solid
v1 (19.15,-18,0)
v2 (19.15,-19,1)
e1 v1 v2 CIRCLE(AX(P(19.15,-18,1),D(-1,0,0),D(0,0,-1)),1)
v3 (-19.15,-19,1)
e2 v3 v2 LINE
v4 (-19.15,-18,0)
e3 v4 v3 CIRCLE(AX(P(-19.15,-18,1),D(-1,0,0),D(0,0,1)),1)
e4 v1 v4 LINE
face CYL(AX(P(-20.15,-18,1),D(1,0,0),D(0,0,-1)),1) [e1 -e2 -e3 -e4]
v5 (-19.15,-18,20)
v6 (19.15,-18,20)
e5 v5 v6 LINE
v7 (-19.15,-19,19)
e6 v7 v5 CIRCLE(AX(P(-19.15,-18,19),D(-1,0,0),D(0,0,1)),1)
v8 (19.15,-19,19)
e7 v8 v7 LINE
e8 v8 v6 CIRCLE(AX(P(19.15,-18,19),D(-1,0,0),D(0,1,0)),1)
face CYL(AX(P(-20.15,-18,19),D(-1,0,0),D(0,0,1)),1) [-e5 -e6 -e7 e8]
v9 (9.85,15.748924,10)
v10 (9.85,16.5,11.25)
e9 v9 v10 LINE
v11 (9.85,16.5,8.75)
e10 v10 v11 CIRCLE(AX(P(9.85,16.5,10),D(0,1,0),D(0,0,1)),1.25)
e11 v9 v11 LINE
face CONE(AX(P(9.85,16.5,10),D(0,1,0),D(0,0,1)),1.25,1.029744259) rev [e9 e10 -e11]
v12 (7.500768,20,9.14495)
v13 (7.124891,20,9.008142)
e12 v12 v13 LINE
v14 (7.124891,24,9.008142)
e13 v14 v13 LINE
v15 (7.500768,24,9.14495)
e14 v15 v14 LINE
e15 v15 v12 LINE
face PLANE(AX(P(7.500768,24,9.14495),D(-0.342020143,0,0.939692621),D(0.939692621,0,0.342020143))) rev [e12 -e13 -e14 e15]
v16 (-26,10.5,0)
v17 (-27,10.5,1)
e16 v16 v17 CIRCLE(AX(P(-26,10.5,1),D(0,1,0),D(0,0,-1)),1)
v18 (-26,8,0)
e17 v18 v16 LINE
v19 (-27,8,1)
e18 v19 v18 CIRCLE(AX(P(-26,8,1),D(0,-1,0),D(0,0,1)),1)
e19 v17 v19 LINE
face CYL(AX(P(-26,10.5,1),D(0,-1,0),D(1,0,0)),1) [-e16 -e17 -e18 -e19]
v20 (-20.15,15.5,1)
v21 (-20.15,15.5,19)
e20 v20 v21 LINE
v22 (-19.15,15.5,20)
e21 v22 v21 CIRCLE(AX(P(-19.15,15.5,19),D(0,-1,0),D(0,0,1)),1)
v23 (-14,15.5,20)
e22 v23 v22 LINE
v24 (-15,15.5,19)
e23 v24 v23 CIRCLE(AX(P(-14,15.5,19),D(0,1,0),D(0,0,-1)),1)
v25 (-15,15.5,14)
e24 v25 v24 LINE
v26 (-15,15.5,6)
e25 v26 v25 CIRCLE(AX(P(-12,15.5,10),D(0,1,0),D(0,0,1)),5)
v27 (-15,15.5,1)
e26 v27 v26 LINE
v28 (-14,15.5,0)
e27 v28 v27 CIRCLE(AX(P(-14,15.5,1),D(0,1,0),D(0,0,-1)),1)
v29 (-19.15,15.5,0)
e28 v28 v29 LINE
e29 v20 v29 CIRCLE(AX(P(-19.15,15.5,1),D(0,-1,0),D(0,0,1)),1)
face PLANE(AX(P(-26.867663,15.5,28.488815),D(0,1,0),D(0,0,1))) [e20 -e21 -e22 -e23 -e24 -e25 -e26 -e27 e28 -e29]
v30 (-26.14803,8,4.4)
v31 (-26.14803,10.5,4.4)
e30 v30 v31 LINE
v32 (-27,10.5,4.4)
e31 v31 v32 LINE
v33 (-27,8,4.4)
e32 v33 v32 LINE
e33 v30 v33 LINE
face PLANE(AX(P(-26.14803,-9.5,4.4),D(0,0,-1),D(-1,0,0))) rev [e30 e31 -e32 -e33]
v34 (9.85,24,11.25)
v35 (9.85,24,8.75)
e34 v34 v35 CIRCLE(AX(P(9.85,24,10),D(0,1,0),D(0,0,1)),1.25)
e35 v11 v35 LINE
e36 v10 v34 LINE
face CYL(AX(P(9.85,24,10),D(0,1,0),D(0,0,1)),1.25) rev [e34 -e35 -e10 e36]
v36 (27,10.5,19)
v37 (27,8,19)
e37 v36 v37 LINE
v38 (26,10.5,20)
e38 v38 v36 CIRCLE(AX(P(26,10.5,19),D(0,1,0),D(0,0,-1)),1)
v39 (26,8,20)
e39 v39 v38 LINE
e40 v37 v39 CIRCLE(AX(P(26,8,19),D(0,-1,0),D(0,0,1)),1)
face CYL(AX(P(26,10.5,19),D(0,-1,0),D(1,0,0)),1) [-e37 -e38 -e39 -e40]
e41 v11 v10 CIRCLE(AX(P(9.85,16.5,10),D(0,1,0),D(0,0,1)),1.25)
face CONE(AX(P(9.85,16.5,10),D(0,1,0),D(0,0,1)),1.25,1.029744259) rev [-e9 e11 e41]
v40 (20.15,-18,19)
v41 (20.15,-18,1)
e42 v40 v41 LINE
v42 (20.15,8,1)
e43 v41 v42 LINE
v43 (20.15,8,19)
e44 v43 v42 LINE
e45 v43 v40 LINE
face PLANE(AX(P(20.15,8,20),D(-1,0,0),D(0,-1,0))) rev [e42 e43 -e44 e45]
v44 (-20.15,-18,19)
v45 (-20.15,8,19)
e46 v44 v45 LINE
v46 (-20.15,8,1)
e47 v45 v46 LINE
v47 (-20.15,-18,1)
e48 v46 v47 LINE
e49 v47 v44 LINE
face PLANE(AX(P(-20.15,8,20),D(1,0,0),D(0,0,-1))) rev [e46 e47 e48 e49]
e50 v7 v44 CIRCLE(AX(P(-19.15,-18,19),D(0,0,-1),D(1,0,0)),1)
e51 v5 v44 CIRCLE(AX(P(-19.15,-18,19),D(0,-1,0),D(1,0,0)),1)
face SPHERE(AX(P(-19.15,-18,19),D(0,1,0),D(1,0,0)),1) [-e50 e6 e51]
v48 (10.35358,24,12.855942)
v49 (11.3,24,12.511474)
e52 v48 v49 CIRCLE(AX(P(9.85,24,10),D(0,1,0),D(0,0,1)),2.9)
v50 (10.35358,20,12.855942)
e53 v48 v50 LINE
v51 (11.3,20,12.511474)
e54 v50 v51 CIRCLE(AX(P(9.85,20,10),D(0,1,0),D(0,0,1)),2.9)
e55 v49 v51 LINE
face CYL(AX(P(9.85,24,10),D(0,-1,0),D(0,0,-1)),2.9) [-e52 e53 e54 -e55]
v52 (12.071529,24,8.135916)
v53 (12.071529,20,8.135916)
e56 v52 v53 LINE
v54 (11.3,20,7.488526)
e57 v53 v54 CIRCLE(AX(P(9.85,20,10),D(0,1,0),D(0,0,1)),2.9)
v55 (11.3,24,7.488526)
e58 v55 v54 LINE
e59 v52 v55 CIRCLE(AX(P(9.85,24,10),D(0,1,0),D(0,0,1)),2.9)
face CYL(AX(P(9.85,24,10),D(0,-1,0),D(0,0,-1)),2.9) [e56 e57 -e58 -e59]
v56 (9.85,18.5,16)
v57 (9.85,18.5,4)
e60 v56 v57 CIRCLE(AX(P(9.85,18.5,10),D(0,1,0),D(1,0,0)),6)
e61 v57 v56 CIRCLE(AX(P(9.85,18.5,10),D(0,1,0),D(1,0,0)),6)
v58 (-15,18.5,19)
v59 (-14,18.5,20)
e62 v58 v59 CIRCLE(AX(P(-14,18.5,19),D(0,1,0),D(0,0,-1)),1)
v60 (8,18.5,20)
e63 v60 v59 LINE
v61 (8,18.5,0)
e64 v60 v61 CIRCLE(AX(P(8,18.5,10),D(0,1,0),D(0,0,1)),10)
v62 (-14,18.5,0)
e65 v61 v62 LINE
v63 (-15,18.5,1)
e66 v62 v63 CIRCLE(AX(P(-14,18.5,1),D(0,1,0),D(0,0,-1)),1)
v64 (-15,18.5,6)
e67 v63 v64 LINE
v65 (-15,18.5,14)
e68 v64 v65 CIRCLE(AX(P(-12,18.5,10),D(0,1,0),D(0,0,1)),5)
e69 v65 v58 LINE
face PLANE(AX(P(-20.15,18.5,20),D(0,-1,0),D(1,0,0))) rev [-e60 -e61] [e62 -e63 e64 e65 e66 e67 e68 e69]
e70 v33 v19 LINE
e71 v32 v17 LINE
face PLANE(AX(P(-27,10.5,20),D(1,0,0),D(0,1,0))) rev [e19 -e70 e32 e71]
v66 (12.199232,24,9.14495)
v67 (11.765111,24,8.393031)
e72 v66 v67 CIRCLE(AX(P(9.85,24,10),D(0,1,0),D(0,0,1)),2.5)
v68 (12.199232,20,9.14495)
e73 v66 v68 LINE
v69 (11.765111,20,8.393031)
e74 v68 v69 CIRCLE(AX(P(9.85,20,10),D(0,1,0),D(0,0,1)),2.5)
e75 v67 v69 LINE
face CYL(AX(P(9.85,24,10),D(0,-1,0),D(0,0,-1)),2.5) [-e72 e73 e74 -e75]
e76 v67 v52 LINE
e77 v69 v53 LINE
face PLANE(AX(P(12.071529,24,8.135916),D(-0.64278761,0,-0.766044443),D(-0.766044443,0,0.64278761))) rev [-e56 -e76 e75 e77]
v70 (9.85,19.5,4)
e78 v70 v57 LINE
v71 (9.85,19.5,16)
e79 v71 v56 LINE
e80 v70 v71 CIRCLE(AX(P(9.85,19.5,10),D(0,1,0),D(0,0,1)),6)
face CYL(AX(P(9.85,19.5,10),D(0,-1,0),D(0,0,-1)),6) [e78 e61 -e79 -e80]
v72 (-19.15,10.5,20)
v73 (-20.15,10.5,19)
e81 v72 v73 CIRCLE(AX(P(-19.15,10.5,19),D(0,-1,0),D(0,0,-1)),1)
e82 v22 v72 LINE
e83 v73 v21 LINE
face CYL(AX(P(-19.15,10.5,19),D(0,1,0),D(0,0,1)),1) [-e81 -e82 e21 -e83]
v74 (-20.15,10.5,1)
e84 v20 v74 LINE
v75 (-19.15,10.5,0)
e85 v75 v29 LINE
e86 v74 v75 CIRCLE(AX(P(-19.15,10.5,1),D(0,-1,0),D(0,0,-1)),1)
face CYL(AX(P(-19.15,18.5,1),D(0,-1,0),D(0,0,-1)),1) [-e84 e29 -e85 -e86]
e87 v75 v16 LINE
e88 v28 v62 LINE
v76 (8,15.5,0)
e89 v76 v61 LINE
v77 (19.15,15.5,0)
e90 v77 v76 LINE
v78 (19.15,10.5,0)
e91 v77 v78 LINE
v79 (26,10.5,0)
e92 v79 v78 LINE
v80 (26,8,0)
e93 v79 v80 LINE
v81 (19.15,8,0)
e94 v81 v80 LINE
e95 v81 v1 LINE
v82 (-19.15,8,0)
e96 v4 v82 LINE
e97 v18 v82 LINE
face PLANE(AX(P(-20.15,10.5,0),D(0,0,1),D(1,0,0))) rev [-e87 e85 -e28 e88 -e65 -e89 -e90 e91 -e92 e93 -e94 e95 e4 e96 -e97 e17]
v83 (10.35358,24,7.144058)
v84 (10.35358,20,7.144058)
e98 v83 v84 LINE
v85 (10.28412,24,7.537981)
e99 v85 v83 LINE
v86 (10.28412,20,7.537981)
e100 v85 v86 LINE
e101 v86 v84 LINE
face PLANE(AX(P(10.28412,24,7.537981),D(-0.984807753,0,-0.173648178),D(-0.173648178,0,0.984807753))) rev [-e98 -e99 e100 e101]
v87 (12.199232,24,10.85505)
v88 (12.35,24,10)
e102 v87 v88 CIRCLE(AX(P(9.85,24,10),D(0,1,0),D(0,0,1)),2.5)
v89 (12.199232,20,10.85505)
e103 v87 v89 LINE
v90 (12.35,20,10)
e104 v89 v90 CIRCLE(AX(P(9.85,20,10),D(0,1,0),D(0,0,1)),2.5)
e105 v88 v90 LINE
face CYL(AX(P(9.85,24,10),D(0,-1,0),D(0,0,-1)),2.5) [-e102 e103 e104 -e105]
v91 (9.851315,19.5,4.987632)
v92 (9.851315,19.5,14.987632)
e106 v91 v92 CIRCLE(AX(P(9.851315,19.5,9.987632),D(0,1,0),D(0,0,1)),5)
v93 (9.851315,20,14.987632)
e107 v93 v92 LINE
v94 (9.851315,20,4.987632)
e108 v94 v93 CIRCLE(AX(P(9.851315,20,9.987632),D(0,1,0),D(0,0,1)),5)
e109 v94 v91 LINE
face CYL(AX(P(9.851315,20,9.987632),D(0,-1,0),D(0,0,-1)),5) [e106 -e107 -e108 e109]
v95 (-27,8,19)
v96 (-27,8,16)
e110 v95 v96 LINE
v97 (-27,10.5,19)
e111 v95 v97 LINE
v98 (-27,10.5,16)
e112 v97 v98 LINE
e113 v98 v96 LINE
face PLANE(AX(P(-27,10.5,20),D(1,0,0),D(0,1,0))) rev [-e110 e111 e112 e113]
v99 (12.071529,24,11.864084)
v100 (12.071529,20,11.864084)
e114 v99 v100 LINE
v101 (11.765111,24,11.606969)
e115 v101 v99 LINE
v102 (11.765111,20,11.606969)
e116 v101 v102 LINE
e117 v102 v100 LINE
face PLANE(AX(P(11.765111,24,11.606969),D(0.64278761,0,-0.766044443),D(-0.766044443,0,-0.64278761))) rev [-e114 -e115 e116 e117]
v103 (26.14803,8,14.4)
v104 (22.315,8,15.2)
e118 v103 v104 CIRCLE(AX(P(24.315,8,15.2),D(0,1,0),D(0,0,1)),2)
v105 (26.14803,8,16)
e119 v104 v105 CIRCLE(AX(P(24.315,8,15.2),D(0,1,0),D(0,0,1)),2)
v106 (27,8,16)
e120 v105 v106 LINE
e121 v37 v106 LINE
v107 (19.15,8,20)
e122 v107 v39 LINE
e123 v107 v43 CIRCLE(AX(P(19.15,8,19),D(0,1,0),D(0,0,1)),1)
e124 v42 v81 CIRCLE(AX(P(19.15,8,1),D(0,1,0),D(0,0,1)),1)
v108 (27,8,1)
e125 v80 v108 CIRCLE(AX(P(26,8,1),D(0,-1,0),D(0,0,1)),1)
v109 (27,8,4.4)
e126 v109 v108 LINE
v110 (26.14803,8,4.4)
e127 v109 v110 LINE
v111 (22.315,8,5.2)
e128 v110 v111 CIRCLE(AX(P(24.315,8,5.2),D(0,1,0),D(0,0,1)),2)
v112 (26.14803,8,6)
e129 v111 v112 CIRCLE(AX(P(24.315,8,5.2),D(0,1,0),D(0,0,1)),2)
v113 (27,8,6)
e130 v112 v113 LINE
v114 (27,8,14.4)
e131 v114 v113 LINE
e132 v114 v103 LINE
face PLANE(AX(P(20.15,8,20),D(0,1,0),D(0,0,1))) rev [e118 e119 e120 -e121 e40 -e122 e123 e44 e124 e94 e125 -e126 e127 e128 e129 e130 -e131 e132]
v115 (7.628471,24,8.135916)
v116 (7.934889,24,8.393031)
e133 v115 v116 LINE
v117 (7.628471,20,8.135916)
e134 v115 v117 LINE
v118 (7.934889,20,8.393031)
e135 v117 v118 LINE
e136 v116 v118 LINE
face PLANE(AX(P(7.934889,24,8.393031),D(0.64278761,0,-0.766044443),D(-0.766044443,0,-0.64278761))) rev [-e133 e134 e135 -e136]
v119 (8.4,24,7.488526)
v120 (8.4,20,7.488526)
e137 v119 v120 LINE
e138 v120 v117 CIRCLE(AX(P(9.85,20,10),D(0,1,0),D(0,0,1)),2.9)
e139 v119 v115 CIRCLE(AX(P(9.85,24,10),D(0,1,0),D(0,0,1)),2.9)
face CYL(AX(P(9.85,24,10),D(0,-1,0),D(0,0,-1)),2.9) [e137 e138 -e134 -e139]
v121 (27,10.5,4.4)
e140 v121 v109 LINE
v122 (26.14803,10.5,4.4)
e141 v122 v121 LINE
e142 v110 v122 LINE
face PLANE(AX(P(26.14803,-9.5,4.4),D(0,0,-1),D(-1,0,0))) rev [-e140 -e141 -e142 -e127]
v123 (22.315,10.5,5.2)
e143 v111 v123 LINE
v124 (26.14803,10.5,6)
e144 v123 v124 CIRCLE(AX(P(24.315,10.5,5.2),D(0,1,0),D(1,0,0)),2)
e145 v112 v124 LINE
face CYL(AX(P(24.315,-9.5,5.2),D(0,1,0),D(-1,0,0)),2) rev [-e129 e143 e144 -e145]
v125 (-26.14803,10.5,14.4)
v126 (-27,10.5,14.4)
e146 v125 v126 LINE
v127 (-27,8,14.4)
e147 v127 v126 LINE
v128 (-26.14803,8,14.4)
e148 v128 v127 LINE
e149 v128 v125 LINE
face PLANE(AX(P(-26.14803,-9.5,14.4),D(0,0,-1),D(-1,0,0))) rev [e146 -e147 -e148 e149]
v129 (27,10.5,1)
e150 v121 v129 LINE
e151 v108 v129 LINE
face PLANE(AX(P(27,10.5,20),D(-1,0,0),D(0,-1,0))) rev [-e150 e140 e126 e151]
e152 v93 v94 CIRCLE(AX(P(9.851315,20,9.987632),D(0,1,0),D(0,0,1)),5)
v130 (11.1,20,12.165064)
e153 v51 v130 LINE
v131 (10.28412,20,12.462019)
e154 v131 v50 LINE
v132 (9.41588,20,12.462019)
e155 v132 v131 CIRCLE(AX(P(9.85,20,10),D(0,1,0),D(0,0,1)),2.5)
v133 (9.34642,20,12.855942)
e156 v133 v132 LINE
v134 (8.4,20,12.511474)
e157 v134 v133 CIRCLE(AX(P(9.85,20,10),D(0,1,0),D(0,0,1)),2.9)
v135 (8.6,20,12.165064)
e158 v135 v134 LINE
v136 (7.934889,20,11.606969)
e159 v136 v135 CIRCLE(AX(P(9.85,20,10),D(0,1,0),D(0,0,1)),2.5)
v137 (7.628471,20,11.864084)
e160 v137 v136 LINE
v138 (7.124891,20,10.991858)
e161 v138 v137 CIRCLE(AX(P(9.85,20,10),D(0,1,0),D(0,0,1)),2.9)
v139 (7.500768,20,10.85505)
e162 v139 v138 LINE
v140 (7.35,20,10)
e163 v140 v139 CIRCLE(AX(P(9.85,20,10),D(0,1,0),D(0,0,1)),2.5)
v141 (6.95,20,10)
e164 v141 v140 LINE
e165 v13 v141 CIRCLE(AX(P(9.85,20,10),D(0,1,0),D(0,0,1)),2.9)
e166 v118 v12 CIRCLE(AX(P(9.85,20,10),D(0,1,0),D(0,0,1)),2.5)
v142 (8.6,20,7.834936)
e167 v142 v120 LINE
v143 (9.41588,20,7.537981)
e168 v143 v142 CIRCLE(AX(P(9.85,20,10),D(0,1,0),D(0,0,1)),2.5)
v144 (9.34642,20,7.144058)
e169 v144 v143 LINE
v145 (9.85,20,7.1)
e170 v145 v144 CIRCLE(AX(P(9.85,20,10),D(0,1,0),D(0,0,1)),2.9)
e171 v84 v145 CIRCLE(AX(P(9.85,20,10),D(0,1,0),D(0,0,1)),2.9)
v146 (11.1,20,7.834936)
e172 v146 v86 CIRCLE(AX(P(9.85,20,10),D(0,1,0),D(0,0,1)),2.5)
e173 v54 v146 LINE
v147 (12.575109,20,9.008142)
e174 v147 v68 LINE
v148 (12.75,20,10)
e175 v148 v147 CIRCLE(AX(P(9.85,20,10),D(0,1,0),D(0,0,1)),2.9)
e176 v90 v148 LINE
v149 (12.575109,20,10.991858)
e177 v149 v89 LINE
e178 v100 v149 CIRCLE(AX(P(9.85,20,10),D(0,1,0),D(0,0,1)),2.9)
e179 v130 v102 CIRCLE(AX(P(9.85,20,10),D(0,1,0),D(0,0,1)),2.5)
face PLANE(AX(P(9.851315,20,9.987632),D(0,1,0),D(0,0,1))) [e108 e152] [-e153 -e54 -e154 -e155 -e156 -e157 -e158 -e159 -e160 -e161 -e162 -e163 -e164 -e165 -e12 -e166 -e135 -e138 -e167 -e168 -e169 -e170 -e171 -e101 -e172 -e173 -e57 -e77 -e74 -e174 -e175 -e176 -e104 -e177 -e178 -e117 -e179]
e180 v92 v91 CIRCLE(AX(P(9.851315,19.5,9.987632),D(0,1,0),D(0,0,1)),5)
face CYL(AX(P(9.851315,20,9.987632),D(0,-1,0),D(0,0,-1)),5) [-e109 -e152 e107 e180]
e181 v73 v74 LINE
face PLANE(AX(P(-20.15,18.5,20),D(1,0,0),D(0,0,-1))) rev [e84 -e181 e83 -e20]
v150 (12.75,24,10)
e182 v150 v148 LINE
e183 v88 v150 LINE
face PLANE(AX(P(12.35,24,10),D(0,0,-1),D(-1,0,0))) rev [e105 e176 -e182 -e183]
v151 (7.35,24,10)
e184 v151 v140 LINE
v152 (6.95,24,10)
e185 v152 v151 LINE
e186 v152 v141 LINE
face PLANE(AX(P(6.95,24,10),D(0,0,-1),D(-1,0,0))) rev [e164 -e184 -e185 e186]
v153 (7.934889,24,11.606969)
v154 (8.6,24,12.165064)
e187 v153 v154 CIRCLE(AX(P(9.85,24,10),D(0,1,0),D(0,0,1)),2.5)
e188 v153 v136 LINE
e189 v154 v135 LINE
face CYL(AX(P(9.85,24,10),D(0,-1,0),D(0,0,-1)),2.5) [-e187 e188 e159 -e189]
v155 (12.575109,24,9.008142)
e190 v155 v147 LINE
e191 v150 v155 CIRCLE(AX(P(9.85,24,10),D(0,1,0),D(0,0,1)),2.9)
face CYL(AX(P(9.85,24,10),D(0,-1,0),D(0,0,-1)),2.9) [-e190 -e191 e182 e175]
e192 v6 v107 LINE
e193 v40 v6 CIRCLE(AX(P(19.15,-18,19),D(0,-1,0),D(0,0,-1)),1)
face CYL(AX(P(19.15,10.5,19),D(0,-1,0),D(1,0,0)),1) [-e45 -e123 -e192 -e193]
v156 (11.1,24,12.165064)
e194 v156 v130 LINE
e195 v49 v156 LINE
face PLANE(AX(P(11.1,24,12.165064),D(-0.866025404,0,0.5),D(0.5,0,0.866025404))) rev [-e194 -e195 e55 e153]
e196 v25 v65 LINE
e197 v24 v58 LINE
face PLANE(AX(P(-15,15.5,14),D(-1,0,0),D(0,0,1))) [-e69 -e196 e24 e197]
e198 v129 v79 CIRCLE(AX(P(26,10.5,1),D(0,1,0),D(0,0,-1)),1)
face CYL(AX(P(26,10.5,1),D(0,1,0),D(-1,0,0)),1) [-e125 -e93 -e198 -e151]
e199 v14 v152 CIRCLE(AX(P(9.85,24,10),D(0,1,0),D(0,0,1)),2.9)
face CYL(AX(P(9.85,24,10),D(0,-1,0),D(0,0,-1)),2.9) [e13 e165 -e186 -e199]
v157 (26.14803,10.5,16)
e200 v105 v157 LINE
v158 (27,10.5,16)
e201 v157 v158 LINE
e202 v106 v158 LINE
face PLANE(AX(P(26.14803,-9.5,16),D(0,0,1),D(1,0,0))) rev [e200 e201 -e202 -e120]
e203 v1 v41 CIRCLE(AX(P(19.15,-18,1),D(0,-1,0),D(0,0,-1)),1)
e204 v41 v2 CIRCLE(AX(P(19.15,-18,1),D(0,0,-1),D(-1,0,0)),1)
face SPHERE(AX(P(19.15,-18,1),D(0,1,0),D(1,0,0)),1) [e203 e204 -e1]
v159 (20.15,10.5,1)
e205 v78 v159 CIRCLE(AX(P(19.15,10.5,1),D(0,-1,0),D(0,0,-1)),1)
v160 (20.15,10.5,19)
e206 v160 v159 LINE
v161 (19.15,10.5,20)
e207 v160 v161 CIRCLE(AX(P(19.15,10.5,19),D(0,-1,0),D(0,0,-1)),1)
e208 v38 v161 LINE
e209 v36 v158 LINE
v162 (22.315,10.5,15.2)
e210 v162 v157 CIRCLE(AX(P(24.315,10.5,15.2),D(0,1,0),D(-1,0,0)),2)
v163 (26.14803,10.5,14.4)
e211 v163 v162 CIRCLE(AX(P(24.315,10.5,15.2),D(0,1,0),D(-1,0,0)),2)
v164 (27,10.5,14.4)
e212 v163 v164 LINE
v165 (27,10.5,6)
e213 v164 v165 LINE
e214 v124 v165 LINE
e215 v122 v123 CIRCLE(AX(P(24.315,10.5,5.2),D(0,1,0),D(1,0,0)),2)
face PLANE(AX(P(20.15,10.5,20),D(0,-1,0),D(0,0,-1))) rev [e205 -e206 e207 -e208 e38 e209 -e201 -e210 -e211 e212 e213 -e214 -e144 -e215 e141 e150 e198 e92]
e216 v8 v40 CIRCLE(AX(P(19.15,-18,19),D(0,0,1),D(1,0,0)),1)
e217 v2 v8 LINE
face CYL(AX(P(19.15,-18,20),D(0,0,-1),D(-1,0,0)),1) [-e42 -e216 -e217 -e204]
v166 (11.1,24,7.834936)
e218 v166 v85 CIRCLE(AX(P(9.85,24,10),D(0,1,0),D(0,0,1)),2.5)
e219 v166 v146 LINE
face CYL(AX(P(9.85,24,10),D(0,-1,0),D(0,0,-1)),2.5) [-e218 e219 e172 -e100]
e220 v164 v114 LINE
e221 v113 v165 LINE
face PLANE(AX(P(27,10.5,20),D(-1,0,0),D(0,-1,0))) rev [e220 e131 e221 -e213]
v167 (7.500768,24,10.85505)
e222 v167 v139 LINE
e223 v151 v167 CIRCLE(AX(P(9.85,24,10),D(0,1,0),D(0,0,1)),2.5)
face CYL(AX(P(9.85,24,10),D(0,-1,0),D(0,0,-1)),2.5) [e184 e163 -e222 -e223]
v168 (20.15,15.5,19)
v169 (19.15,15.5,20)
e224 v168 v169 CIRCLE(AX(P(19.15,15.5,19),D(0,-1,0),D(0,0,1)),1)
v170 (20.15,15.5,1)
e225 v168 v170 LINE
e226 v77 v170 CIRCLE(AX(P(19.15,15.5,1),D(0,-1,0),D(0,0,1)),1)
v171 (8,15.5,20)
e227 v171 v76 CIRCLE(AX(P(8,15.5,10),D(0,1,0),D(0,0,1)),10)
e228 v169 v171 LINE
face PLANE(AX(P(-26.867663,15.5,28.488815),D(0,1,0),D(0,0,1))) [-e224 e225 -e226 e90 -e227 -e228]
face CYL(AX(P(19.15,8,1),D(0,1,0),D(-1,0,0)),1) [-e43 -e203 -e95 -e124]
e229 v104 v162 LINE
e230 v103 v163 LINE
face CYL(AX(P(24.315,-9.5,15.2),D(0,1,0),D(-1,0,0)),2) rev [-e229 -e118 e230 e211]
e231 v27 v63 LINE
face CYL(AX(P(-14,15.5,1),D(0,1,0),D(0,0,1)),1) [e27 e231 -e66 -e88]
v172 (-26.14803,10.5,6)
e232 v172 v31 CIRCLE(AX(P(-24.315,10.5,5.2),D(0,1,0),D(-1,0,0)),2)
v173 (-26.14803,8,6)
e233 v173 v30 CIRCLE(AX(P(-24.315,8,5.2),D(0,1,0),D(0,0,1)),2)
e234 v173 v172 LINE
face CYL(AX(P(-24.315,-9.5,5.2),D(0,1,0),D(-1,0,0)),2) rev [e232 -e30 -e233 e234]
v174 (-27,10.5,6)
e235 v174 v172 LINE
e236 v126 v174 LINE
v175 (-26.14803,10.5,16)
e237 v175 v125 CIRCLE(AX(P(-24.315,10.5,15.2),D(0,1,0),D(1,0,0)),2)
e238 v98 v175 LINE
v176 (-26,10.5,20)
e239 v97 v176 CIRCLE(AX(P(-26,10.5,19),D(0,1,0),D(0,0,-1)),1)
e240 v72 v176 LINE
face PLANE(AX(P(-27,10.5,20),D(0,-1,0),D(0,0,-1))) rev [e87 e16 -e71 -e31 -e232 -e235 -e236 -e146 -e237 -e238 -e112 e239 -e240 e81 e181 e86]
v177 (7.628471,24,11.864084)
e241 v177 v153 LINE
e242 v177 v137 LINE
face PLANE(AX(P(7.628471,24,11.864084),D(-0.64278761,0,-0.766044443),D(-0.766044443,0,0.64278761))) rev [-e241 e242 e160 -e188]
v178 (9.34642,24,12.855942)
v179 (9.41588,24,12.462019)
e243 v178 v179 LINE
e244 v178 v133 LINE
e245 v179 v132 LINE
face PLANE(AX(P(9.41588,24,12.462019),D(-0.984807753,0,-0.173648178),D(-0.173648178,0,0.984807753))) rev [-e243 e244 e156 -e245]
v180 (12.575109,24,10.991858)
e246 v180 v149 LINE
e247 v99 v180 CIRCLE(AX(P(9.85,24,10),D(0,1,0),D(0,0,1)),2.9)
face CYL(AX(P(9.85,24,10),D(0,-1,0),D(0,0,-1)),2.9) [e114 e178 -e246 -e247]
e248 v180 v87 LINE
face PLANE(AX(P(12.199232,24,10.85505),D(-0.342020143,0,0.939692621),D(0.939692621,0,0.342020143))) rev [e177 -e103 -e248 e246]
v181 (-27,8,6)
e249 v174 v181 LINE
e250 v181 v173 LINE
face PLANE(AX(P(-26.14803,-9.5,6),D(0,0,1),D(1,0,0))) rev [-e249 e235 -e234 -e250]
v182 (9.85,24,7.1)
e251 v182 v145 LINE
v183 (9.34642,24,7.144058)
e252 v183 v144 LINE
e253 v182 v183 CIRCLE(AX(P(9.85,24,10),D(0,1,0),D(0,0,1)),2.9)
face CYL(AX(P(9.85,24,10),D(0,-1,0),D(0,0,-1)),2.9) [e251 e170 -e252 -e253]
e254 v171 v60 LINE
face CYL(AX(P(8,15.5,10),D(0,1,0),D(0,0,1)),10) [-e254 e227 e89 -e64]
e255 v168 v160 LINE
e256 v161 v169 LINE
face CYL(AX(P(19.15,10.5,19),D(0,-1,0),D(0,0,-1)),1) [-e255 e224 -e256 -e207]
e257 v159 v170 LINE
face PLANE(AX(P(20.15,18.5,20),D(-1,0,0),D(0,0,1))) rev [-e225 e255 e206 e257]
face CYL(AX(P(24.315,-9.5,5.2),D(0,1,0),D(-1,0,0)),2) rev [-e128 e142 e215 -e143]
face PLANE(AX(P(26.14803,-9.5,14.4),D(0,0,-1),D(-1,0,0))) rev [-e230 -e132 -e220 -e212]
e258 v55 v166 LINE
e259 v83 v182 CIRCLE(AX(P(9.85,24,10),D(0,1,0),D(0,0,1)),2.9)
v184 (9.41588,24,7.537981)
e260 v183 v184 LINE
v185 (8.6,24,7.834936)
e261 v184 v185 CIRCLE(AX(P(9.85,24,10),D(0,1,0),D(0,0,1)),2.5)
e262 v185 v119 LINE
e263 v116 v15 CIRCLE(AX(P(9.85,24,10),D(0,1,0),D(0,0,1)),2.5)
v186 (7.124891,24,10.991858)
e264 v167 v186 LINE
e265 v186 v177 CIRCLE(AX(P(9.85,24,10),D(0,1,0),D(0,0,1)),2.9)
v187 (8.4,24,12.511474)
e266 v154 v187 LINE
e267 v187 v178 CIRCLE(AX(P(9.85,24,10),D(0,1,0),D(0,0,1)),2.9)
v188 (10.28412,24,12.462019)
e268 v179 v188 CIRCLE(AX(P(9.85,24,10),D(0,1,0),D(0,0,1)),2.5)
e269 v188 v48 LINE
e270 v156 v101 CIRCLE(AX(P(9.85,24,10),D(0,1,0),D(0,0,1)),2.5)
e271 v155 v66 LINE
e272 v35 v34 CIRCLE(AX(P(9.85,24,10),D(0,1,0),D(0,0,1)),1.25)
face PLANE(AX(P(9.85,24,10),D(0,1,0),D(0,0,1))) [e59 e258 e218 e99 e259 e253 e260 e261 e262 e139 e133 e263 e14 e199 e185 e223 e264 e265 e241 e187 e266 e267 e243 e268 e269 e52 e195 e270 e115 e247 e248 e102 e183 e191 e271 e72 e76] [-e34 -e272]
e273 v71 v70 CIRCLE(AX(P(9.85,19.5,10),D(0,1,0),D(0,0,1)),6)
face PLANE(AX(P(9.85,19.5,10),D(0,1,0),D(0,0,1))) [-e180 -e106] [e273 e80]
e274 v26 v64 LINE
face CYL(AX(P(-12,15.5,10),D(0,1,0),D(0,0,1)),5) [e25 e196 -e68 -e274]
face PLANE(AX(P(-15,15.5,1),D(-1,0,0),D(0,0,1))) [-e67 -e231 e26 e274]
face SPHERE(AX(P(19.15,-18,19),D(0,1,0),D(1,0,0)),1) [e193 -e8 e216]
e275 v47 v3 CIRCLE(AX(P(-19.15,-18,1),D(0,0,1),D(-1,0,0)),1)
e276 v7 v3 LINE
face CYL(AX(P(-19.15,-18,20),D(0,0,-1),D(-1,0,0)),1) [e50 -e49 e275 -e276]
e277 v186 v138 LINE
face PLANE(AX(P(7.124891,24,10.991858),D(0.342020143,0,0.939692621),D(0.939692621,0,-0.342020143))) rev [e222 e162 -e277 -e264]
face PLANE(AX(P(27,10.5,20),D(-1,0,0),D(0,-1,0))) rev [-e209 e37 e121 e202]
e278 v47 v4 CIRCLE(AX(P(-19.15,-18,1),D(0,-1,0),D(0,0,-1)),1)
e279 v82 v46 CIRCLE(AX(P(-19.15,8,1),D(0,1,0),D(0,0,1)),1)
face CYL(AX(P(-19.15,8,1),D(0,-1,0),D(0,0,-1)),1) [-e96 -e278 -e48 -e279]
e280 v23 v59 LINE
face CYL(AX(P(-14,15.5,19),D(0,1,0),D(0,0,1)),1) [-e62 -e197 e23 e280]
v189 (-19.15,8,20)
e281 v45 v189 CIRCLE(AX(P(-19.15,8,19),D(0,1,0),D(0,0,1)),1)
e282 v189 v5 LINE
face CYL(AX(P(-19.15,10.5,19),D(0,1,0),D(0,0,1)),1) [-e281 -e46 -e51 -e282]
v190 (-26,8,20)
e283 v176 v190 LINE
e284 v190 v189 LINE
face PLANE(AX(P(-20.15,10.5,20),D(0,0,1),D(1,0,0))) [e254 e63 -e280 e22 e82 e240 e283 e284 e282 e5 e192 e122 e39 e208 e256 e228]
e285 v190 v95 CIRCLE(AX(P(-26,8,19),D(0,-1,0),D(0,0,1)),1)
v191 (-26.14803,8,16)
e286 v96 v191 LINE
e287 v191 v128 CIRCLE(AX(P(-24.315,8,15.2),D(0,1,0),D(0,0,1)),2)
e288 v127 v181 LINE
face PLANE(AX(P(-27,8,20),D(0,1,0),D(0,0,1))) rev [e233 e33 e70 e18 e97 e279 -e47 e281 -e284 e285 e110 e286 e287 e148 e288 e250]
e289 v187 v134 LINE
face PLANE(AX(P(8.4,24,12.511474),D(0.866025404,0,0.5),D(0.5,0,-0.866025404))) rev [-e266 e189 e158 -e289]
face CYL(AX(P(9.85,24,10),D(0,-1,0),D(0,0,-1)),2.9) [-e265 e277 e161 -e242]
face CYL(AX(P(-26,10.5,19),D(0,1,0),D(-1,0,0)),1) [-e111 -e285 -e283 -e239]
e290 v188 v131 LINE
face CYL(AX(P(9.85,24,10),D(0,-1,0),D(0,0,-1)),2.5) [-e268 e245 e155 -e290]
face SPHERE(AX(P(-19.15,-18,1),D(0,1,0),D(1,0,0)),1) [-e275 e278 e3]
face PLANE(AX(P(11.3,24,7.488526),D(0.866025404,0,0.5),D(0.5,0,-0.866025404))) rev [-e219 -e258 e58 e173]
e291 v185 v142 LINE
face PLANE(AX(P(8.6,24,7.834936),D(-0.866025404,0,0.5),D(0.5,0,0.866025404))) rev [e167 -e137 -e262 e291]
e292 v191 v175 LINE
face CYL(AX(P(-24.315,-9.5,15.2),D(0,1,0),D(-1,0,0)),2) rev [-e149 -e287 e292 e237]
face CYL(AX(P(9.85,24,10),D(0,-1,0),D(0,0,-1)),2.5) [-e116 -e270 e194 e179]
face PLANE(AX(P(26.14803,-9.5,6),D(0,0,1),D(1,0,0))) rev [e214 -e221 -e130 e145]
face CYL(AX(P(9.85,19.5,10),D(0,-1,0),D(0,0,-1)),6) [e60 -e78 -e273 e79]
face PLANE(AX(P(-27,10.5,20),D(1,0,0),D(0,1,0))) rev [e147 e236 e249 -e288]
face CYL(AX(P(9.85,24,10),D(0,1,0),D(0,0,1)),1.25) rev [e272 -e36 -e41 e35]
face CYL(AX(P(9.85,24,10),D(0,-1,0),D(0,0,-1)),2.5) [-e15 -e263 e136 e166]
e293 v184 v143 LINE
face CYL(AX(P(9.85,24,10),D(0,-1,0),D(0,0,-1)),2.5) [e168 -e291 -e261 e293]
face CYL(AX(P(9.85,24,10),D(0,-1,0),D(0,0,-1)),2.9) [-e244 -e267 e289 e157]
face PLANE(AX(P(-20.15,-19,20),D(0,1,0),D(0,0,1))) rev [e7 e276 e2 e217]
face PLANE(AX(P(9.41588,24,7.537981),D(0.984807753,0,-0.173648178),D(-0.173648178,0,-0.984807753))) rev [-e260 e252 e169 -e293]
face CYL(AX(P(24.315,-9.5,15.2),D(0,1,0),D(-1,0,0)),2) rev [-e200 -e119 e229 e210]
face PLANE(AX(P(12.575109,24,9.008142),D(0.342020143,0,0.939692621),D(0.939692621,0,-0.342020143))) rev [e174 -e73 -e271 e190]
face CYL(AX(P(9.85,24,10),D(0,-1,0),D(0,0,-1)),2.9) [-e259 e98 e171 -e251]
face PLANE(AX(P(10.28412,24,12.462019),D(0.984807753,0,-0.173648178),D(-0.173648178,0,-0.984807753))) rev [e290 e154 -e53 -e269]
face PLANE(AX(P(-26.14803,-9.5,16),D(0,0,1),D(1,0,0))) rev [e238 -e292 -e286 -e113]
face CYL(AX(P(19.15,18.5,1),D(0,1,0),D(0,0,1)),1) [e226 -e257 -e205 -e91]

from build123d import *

# Parameters (mm, degrees)
EXTRUDE_1_DEPTH        = 20
FILLET_1_R             = 1
CUT_EXTRUDE_1_DEPTH    = 20
SKETCH_3_W             = 51.867663345
SKETCH_3_H             = 35.261757523
CUT_EXTRUDE_2_DEPTH    = 3
SKETCH_4_R             = 6
EXTRUDE_2_DEPTH        = 1
SKETCH_5_R             = 5
EXTRUDE_3_DEPTH        = 0.5
SKETCH_6_R             = 1
EXTRUDE_4_DEPTH        = 4
HOLE_WIZARD_M3_1_D     = 2.5
HOLE_WIZARD_M3_1_DEPTH = 7.5
HOLE_WIZARD_M3_1_TIP   = 0.751075774


with BuildPart() as part:
    # 草图1 → 凸台-拉伸1 (new body)
    with BuildSketch(Plane.XY):
        Polygon((20.15, 8), (27, 8), (27, 10.5), (20.15, 10.5), (20.15, 18.5), (-20.15, 18.5), (-20.15, 10.5), (-27, 10.5), (-27, 8), (-20.15, 8), (-20.15, -19), (20.15, -19), align=None)
    extrude(amount=EXTRUDE_1_DEPTH)

    # 圆角1
    fillet_1_edges = [part.edges().sort_by_distance(p)[0] for p in [
        (-27, 9.25, 20),
        (20.15, 14.5, 0),
        (27, 9.25, 0),
        (20.15, -5.5, 0),
        (0, -19, 0),
        (-20.15, -5.5, 0),
        (-27, 9.25, 0),
        (-20.15, 14.5, 0),
        (-20.15, -5.5, 20),
        (0, -19, 20),
        (-20.15, 18.5, 10),
        (20.15, 18.5, 10),
        (20.15, -19, 10),
        (-20.15, -19, 10),
        (20.15, -5.5, 20),
        (27, 9.25, 20),
        (20.15, 14.5, 20),
        (-20.15, 14.5, 20),
    ]]
    fillet(fillet_1_edges, radius=FILLET_1_R)

    # 草图2 → 切除-拉伸1 (cut)
    with BuildSketch(Plane(origin=(0, 10.5, 0), x_dir=(1, 0, 0), z_dir=(0, 1, 0))):
        with BuildLine():
            Line((-26.148030278, -4.4), (-29.222738853, -4.4))
            Line((-29.222738853, -4.4), (-29.222738853, -6))
            Line((-29.222738853, -6), (-26.148030278, -6))
            ThreePointArc((-26.148030278, -6), (-22.315, -5.2), (-26.148030278, -4.4))
        make_face()
        with BuildLine():
            Line((-26.148030278, -14.4), (-29.222738853, -14.4))
            Line((-29.222738853, -14.4), (-29.222738853, -16))
            Line((-29.222738853, -16), (-26.148030278, -16))
            ThreePointArc((-26.148030278, -16), (-22.315, -15.2), (-26.148030278, -14.4))
        make_face()
        with BuildLine():
            Line((26.148030278, -16), (29.222738853, -16))
            Line((29.222738853, -16), (29.222738853, -14.4))
            Line((29.222738853, -14.4), (26.148030278, -14.4))
            ThreePointArc((26.148030278, -14.4), (22.315, -15.2), (26.148030278, -16))
        make_face()
        with BuildLine():
            Line((29.222738853, -4.4), (29.222738853, -6))
            Line((29.222738853, -6), (26.148030278, -6))
            ThreePointArc((26.148030278, -6), (22.315, -5.2), (26.148030278, -4.4))
            Line((26.148030278, -4.4), (29.222738853, -4.4))
        make_face()
    extrude(amount=-CUT_EXTRUDE_1_DEPTH, mode=Mode.SUBTRACT)

    # 草图3 → 切除-拉伸2 (cut)
    with BuildSketch(Plane(origin=(0, 18.5, 0), x_dir=(1, 0, 0), z_dir=(0, 1, 0))):
        with Locations((-0.933831673, -10.85793672)):
            Rectangle(SKETCH_3_W, SKETCH_3_H)
        with BuildLine():
            Line((-14, 0), (8, 0))
            ThreePointArc((8, 0), (18, -10), (8, -20))
            Line((8, -20), (-14, -20))
            ThreePointArc((-14, -20), (-14.707106781, -19.707106781), (-15, -19))
            Line((-15, -19), (-15, -14))
            ThreePointArc((-15, -14), (-17, -10), (-15, -6))
            Line((-15, -6), (-15, -1))
            ThreePointArc((-15, -1), (-14.707106781, -0.292893219), (-14, 0))
        make_face(mode=Mode.SUBTRACT)
    extrude(amount=-CUT_EXTRUDE_2_DEPTH, mode=Mode.SUBTRACT)

    # 草图4 → 凸台-拉伸2 (add)
    with BuildSketch(Plane(origin=(0, 18.5, 0), x_dir=(1, 0, 0), z_dir=(0, 1, 0))):
        with Locations((9.85, -10)):
            Circle(SKETCH_4_R)
    extrude(amount=EXTRUDE_2_DEPTH)

    # 草图5 → 凸台-拉伸3 (add)
    with BuildSketch(Plane(origin=(0, 19.5, 0), x_dir=(1, 0, 0), z_dir=(0, 1, 0))):
        with Locations(Location((9.851314919, -9.987632383, 0), (0, 0, 270))):
            Circle(SKETCH_5_R)
    extrude(amount=EXTRUDE_3_DEPTH)

    # 草图6 → 凸台-拉伸4 (add)
    with BuildSketch(Plane(origin=(0, 20, 0), x_dir=(1, 0, 0), z_dir=(0, 1, 0))):
        with BuildLine():
            Line((10.284120444, -7.537980617), (10.353579715, -7.144057516))
            ThreePointArc((10.353579715, -7.144057516), (9.85, -7.1), (9.346420285, -7.144057516))
            Line((9.346420285, -7.144057516), (9.415879556, -7.537980617))
            ThreePointArc((9.415879556, -7.537980617), (8.994949642, -7.650768448), (8.6, -7.834936491))
            Line((8.6, -7.834936491), (8.4, -7.488526329))
            ThreePointArc((8.4, -7.488526329), (7.985915932, -7.778471115), (7.628471115, -8.135915932))
            Line((7.628471115, -8.135915932), (7.934888892, -8.393030976))
            ThreePointArc((7.934888892, -8.393030976), (7.684936491, -8.75), (7.500768448, -9.144949642))
            Line((7.500768448, -9.144949642), (7.1248914, -9.008141584))
            ThreePointArc((7.1248914, -9.008141584), (6.994057516, -9.496420285), (6.95, -10))
            Line((6.95, -10), (7.35, -10))
            ThreePointArc((7.35, -10), (7.387980617, -10.434120444), (7.500768448, -10.855050358))
            Line((7.500768448, -10.855050358), (7.1248914, -10.991858416))
            ThreePointArc((7.1248914, -10.991858416), (7.338526329, -11.45), (7.628471115, -11.864084068))
            Line((7.628471115, -11.864084068), (7.934888892, -11.606969024))
            ThreePointArc((7.934888892, -11.606969024), (8.243030976, -11.915111108), (8.6, -12.165063509))
            Line((8.6, -12.165063509), (8.4, -12.511473671))
            ThreePointArc((8.4, -12.511473671), (8.858141584, -12.7251086), (9.346420285, -12.855942484))
            Line((9.346420285, -12.855942484), (9.415879556, -12.462019383))
            ThreePointArc((9.415879556, -12.462019383), (9.85, -12.5), (10.284120444, -12.462019383))
            Line((10.284120444, -12.462019383), (10.353579715, -12.855942484))
            ThreePointArc((10.353579715, -12.855942484), (10.841858416, -12.7251086), (11.3, -12.511473671))
            Line((11.3, -12.511473671), (11.1, -12.165063509))
            ThreePointArc((11.1, -12.165063509), (11.456969024, -11.915111108), (11.765111108, -11.606969024))
            Line((11.765111108, -11.606969024), (12.071528885, -11.864084068))
            ThreePointArc((12.071528885, -11.864084068), (12.361473671, -11.45), (12.5751086, -10.991858416))
            Line((12.5751086, -10.991858416), (12.199231552, -10.855050358))
            ThreePointArc((12.199231552, -10.855050358), (12.312019383, -10.434120444), (12.35, -10))
            Line((12.35, -10), (12.75, -10))
            ThreePointArc((12.75, -10), (12.705942484, -9.496420285), (12.5751086, -9.008141584))
            Line((12.5751086, -9.008141584), (12.199231552, -9.144949642))
            ThreePointArc((12.199231552, -9.144949642), (12.015063509, -8.75), (11.765111108, -8.393030976))
            Line((11.765111108, -8.393030976), (12.071528885, -8.135915932))
            ThreePointArc((12.071528885, -8.135915932), (11.714084068, -7.778471115), (11.3, -7.488526329))
            Line((11.3, -7.488526329), (11.1, -7.834936491))
            ThreePointArc((11.1, -7.834936491), (10.705050358, -7.650768448), (10.284120444, -7.537980617))
        make_face()
        with Locations(Location((9.85, -10, 0), (0, 0, 270))):
            Circle(SKETCH_6_R, mode=Mode.SUBTRACT)
    extrude(amount=EXTRUDE_4_DEPTH)

    # M3 螺纹孔1
    with Locations(Plane(origin=(9.85, 24, 10), x_dir=(0, 0, 1), z_dir=(0, 1, 0))):
        with Locations((0, 0)):
            Hole(HOLE_WIZARD_M3_1_D / 2, depth=HOLE_WIZARD_M3_1_DEPTH)
            with Locations((0, 0, -(HOLE_WIZARD_M3_1_DEPTH + HOLE_WIZARD_M3_1_TIP / 2))):  # 118° drill point
                Cone(0, HOLE_WIZARD_M3_1_D / 2, HOLE_WIZARD_M3_1_TIP, mode=Mode.SUBTRACT)


solid = part.part
